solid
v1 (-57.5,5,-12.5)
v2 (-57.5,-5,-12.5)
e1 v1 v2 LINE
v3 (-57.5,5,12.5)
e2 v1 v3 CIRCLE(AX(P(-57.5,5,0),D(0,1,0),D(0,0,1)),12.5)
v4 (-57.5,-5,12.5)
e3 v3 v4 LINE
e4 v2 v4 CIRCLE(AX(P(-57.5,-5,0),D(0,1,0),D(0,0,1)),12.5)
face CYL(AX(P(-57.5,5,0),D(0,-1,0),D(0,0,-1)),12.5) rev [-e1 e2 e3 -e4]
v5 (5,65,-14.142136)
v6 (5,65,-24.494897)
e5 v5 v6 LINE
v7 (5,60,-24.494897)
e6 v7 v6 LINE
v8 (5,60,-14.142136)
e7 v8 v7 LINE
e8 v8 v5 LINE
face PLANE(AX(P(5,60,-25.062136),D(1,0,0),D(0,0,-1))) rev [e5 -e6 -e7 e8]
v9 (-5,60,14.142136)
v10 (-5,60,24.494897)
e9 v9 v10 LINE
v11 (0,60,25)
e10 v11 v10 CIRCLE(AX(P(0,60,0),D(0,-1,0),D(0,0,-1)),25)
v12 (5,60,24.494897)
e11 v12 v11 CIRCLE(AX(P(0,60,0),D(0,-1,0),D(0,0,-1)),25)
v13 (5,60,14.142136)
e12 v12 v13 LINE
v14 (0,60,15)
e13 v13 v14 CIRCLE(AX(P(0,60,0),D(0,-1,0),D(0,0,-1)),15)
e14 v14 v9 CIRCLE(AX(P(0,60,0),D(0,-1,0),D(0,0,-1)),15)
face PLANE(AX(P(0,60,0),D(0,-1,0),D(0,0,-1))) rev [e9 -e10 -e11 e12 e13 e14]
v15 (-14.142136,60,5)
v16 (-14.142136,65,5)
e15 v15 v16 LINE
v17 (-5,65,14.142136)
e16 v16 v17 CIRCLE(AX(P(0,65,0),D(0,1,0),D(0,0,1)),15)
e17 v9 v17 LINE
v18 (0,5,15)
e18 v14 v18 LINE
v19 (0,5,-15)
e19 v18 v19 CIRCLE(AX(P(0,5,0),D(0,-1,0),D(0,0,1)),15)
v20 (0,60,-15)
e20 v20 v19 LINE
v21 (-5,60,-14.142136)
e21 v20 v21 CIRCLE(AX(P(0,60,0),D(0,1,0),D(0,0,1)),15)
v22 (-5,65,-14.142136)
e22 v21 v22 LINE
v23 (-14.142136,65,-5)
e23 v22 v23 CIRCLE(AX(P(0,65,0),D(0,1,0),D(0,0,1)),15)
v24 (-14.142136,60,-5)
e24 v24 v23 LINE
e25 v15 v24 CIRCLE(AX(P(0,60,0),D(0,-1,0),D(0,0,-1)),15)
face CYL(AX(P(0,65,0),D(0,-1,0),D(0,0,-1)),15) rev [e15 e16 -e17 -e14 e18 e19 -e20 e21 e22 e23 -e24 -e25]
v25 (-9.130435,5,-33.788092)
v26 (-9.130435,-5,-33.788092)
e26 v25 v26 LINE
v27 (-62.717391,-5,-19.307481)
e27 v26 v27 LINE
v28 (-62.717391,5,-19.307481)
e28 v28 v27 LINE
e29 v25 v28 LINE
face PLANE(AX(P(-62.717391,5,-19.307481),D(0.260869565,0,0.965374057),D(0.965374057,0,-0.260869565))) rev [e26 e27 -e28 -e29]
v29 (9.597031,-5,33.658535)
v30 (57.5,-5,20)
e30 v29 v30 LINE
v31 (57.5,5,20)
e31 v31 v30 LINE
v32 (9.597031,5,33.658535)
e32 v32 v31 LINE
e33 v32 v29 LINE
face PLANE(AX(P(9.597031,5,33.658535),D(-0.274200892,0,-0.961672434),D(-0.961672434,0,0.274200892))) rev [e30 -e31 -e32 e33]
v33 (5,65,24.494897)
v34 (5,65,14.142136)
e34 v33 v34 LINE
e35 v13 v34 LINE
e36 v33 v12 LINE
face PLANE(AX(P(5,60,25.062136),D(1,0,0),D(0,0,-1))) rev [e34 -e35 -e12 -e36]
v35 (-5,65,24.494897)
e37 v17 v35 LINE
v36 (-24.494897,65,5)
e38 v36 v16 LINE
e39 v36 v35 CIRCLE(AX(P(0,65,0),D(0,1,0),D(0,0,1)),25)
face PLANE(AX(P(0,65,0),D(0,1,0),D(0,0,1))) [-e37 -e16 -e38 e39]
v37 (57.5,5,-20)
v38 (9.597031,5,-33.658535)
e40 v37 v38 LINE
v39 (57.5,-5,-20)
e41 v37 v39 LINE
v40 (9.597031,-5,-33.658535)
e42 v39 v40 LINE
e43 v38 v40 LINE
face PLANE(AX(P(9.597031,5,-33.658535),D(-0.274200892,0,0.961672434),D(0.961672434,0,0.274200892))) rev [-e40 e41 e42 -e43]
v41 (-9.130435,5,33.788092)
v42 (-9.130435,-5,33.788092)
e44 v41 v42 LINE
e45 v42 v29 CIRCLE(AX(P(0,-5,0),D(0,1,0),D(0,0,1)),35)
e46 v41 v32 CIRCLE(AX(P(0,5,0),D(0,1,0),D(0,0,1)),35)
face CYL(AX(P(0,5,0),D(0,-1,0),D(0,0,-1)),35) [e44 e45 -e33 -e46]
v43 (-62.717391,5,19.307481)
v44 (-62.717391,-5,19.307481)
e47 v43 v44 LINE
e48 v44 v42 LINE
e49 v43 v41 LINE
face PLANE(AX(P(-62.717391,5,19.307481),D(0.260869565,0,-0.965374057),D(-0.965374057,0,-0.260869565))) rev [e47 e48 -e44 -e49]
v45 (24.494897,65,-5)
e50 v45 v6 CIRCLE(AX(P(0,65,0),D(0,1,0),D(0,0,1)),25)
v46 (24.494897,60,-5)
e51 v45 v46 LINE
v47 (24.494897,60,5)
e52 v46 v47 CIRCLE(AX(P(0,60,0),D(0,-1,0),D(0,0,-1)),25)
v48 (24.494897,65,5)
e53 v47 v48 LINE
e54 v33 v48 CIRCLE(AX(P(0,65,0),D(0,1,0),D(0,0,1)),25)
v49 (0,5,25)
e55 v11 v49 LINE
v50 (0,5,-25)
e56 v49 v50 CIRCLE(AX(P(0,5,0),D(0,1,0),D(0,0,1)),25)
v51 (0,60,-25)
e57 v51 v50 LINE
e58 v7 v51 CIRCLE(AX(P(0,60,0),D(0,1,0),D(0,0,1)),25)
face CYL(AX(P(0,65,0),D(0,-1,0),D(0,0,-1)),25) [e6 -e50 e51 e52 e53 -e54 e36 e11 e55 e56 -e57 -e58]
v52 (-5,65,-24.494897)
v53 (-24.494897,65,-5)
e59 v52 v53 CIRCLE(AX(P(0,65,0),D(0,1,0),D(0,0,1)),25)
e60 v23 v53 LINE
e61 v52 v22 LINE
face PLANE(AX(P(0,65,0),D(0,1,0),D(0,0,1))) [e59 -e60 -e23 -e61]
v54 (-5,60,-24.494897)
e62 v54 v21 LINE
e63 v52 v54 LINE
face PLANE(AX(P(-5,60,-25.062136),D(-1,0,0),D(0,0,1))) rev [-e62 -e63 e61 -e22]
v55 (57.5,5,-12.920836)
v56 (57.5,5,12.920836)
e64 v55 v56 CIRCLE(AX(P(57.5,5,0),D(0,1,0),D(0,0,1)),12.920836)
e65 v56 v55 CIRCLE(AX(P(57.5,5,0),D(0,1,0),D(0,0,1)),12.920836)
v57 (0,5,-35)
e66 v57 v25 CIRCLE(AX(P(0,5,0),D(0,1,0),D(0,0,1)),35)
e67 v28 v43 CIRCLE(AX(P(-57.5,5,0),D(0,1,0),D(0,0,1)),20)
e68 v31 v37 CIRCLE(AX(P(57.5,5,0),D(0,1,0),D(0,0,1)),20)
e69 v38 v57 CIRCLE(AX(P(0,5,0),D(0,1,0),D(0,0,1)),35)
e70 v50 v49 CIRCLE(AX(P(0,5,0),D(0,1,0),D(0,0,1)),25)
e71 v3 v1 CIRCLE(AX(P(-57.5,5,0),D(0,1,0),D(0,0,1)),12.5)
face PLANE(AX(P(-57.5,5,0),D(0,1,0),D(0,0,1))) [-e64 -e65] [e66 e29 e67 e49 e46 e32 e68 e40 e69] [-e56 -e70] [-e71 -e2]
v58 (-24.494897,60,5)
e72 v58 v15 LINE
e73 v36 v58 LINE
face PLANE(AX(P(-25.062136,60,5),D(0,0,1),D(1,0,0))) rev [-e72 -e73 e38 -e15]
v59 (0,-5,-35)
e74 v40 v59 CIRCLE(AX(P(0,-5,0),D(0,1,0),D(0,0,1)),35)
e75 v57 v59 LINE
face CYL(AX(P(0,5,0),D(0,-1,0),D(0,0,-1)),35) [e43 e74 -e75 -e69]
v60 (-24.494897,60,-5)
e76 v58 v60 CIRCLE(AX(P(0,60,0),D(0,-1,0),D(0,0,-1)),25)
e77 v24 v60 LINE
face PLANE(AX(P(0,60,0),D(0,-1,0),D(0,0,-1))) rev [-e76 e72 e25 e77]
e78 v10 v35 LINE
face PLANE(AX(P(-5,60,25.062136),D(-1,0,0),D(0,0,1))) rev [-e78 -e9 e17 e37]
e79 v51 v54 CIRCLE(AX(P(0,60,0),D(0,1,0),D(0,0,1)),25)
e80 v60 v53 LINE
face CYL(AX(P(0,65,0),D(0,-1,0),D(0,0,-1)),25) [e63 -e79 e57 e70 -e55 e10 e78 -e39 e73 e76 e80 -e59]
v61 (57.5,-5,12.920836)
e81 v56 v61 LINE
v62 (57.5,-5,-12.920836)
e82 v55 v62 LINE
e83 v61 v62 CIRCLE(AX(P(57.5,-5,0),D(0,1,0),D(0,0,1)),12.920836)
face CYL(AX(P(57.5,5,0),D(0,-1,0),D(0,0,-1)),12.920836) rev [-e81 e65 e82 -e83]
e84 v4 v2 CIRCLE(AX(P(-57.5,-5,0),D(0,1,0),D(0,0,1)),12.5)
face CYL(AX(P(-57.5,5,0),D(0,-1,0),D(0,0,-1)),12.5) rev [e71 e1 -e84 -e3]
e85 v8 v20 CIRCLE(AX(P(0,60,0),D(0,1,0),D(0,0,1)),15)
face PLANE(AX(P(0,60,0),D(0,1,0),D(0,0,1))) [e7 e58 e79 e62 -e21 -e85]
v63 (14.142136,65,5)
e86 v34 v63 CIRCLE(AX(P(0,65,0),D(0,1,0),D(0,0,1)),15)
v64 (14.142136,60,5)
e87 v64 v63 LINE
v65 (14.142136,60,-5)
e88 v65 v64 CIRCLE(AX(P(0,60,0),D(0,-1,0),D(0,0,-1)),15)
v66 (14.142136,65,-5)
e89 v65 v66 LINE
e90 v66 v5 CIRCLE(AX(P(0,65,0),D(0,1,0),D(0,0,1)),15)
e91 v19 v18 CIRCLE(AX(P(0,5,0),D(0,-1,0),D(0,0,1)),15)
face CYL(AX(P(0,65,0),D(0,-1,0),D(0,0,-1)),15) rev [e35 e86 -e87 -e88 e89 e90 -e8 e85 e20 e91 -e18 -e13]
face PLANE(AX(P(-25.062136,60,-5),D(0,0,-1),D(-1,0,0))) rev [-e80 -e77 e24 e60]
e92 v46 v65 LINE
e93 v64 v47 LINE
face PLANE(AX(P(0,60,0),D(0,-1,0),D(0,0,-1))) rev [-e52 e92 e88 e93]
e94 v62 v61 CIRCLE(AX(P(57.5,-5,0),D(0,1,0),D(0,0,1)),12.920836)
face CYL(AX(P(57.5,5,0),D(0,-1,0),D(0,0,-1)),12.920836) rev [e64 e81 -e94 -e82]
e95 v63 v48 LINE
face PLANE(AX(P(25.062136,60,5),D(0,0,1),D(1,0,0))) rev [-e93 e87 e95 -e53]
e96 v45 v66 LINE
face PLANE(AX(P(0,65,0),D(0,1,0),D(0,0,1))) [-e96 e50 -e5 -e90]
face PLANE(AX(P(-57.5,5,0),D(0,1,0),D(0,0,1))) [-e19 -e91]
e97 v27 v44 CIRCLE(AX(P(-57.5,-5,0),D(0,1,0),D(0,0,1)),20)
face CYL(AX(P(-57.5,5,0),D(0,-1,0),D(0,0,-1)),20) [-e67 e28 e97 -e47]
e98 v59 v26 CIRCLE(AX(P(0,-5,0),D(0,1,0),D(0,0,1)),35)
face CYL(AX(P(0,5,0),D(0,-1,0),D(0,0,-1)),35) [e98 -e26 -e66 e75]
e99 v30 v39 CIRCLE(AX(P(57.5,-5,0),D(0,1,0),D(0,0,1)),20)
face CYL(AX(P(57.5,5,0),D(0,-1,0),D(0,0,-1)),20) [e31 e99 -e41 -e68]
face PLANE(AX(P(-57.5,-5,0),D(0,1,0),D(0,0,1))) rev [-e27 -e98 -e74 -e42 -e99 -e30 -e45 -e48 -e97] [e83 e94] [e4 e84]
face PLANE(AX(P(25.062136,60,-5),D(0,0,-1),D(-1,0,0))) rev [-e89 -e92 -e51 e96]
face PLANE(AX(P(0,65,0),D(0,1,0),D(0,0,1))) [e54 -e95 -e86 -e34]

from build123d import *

# Parameters (mm, degrees)
FLANGE_PROFILE_R       = 12.5
FLANGE_PROFILE_R_2     = 12.920835642
FLANGE_PLATE_DEPTH     = 5
HUB_PROFILE_R          = 25
HUB_PROFILE_R_2        = 15
HUB_50_BORE_30_DEPTH   = 60
CROSS_SLOT_PROFILE_W   = 10
CROSS_SLOT_PROFILE_H   = 10.92
CROSS_SLOT_PROFILE_W_2 = 10.92
CROSS_SLOT_PROFILE_H_2 = 10
CROSS_SLOTS_4X10_DEPTH = 5


with BuildPart() as part:
    # Flange Profile → Flange Plate (new, symmetric)
    with BuildSketch(Plane(origin=(0, 0, 0), x_dir=(1, 0, 0), z_dir=(0, 1, 0))):
        with BuildLine():
            Line((-62.717391304, 19.30748114), (-9.130434783, 33.788091995))
            ThreePointArc((-9.130434783, 33.788091995), (0.242124563, 34.9991625), (9.597031237, 33.658535195))
            Line((9.597031237, 33.658535195), (57.5, 20))
            ThreePointArc((57.5, 20), (77.5, 0), (57.5, -20))
            Line((57.5, -20), (9.597031237, -33.658535195))
            ThreePointArc((9.597031237, -33.658535195), (0.242124563, -34.9991625), (-9.130434783, -33.788091995))
            Line((-9.130434783, -33.788091995), (-62.717391304, -19.30748114))
            ThreePointArc((-62.717391304, -19.30748114), (-77.5, 0), (-62.717391304, 19.30748114))
        make_face()
        with Locations(Location((-57.5, 0, 0), (0, 0, 270))):
            Circle(FLANGE_PROFILE_R, mode=Mode.SUBTRACT)
        with Locations(Location((57.5, 0, 0), (0, 0, 270))):
            Circle(FLANGE_PROFILE_R_2, mode=Mode.SUBTRACT)
    extrude(amount=FLANGE_PLATE_DEPTH, both=True)

    # Hub Profile → Hub Ø50 Bore Ø30 (add)
    with BuildSketch(Plane(origin=(0, 5, 0), x_dir=(1, 0, 0), z_dir=(0, 1, 0))):
        with Locations(Location((0, 0, 0), (0, 0, 270))):
            Circle(HUB_PROFILE_R)
        with Locations(Location((0, 0, 0), (0, 0, 270))):
            Circle(HUB_PROFILE_R_2, mode=Mode.SUBTRACT)
    extrude(amount=HUB_50_BORE_30_DEPTH)

    # Cross Slot Profile → Cross Slots 4x10 (cut)
    with BuildSketch(Plane(origin=(0, 65, 0), x_dir=(1, 0, 0), z_dir=(0, 1, 0))):
        with Locations((0, 19.602135624)):
            Rectangle(CROSS_SLOT_PROFILE_W, CROSS_SLOT_PROFILE_H)
        with Locations((19.602135624, 0)):
            Rectangle(CROSS_SLOT_PROFILE_W_2, CROSS_SLOT_PROFILE_H_2)
        with Locations((0, -19.602135624)):
            Rectangle(CROSS_SLOT_PROFILE_W, CROSS_SLOT_PROFILE_H)
        with Locations((-19.602135624, 0)):
            Rectangle(CROSS_SLOT_PROFILE_W_2, CROSS_SLOT_PROFILE_H_2)
    extrude(amount=-CROSS_SLOTS_4X10_DEPTH, mode=Mode.SUBTRACT)


solid = part.part
